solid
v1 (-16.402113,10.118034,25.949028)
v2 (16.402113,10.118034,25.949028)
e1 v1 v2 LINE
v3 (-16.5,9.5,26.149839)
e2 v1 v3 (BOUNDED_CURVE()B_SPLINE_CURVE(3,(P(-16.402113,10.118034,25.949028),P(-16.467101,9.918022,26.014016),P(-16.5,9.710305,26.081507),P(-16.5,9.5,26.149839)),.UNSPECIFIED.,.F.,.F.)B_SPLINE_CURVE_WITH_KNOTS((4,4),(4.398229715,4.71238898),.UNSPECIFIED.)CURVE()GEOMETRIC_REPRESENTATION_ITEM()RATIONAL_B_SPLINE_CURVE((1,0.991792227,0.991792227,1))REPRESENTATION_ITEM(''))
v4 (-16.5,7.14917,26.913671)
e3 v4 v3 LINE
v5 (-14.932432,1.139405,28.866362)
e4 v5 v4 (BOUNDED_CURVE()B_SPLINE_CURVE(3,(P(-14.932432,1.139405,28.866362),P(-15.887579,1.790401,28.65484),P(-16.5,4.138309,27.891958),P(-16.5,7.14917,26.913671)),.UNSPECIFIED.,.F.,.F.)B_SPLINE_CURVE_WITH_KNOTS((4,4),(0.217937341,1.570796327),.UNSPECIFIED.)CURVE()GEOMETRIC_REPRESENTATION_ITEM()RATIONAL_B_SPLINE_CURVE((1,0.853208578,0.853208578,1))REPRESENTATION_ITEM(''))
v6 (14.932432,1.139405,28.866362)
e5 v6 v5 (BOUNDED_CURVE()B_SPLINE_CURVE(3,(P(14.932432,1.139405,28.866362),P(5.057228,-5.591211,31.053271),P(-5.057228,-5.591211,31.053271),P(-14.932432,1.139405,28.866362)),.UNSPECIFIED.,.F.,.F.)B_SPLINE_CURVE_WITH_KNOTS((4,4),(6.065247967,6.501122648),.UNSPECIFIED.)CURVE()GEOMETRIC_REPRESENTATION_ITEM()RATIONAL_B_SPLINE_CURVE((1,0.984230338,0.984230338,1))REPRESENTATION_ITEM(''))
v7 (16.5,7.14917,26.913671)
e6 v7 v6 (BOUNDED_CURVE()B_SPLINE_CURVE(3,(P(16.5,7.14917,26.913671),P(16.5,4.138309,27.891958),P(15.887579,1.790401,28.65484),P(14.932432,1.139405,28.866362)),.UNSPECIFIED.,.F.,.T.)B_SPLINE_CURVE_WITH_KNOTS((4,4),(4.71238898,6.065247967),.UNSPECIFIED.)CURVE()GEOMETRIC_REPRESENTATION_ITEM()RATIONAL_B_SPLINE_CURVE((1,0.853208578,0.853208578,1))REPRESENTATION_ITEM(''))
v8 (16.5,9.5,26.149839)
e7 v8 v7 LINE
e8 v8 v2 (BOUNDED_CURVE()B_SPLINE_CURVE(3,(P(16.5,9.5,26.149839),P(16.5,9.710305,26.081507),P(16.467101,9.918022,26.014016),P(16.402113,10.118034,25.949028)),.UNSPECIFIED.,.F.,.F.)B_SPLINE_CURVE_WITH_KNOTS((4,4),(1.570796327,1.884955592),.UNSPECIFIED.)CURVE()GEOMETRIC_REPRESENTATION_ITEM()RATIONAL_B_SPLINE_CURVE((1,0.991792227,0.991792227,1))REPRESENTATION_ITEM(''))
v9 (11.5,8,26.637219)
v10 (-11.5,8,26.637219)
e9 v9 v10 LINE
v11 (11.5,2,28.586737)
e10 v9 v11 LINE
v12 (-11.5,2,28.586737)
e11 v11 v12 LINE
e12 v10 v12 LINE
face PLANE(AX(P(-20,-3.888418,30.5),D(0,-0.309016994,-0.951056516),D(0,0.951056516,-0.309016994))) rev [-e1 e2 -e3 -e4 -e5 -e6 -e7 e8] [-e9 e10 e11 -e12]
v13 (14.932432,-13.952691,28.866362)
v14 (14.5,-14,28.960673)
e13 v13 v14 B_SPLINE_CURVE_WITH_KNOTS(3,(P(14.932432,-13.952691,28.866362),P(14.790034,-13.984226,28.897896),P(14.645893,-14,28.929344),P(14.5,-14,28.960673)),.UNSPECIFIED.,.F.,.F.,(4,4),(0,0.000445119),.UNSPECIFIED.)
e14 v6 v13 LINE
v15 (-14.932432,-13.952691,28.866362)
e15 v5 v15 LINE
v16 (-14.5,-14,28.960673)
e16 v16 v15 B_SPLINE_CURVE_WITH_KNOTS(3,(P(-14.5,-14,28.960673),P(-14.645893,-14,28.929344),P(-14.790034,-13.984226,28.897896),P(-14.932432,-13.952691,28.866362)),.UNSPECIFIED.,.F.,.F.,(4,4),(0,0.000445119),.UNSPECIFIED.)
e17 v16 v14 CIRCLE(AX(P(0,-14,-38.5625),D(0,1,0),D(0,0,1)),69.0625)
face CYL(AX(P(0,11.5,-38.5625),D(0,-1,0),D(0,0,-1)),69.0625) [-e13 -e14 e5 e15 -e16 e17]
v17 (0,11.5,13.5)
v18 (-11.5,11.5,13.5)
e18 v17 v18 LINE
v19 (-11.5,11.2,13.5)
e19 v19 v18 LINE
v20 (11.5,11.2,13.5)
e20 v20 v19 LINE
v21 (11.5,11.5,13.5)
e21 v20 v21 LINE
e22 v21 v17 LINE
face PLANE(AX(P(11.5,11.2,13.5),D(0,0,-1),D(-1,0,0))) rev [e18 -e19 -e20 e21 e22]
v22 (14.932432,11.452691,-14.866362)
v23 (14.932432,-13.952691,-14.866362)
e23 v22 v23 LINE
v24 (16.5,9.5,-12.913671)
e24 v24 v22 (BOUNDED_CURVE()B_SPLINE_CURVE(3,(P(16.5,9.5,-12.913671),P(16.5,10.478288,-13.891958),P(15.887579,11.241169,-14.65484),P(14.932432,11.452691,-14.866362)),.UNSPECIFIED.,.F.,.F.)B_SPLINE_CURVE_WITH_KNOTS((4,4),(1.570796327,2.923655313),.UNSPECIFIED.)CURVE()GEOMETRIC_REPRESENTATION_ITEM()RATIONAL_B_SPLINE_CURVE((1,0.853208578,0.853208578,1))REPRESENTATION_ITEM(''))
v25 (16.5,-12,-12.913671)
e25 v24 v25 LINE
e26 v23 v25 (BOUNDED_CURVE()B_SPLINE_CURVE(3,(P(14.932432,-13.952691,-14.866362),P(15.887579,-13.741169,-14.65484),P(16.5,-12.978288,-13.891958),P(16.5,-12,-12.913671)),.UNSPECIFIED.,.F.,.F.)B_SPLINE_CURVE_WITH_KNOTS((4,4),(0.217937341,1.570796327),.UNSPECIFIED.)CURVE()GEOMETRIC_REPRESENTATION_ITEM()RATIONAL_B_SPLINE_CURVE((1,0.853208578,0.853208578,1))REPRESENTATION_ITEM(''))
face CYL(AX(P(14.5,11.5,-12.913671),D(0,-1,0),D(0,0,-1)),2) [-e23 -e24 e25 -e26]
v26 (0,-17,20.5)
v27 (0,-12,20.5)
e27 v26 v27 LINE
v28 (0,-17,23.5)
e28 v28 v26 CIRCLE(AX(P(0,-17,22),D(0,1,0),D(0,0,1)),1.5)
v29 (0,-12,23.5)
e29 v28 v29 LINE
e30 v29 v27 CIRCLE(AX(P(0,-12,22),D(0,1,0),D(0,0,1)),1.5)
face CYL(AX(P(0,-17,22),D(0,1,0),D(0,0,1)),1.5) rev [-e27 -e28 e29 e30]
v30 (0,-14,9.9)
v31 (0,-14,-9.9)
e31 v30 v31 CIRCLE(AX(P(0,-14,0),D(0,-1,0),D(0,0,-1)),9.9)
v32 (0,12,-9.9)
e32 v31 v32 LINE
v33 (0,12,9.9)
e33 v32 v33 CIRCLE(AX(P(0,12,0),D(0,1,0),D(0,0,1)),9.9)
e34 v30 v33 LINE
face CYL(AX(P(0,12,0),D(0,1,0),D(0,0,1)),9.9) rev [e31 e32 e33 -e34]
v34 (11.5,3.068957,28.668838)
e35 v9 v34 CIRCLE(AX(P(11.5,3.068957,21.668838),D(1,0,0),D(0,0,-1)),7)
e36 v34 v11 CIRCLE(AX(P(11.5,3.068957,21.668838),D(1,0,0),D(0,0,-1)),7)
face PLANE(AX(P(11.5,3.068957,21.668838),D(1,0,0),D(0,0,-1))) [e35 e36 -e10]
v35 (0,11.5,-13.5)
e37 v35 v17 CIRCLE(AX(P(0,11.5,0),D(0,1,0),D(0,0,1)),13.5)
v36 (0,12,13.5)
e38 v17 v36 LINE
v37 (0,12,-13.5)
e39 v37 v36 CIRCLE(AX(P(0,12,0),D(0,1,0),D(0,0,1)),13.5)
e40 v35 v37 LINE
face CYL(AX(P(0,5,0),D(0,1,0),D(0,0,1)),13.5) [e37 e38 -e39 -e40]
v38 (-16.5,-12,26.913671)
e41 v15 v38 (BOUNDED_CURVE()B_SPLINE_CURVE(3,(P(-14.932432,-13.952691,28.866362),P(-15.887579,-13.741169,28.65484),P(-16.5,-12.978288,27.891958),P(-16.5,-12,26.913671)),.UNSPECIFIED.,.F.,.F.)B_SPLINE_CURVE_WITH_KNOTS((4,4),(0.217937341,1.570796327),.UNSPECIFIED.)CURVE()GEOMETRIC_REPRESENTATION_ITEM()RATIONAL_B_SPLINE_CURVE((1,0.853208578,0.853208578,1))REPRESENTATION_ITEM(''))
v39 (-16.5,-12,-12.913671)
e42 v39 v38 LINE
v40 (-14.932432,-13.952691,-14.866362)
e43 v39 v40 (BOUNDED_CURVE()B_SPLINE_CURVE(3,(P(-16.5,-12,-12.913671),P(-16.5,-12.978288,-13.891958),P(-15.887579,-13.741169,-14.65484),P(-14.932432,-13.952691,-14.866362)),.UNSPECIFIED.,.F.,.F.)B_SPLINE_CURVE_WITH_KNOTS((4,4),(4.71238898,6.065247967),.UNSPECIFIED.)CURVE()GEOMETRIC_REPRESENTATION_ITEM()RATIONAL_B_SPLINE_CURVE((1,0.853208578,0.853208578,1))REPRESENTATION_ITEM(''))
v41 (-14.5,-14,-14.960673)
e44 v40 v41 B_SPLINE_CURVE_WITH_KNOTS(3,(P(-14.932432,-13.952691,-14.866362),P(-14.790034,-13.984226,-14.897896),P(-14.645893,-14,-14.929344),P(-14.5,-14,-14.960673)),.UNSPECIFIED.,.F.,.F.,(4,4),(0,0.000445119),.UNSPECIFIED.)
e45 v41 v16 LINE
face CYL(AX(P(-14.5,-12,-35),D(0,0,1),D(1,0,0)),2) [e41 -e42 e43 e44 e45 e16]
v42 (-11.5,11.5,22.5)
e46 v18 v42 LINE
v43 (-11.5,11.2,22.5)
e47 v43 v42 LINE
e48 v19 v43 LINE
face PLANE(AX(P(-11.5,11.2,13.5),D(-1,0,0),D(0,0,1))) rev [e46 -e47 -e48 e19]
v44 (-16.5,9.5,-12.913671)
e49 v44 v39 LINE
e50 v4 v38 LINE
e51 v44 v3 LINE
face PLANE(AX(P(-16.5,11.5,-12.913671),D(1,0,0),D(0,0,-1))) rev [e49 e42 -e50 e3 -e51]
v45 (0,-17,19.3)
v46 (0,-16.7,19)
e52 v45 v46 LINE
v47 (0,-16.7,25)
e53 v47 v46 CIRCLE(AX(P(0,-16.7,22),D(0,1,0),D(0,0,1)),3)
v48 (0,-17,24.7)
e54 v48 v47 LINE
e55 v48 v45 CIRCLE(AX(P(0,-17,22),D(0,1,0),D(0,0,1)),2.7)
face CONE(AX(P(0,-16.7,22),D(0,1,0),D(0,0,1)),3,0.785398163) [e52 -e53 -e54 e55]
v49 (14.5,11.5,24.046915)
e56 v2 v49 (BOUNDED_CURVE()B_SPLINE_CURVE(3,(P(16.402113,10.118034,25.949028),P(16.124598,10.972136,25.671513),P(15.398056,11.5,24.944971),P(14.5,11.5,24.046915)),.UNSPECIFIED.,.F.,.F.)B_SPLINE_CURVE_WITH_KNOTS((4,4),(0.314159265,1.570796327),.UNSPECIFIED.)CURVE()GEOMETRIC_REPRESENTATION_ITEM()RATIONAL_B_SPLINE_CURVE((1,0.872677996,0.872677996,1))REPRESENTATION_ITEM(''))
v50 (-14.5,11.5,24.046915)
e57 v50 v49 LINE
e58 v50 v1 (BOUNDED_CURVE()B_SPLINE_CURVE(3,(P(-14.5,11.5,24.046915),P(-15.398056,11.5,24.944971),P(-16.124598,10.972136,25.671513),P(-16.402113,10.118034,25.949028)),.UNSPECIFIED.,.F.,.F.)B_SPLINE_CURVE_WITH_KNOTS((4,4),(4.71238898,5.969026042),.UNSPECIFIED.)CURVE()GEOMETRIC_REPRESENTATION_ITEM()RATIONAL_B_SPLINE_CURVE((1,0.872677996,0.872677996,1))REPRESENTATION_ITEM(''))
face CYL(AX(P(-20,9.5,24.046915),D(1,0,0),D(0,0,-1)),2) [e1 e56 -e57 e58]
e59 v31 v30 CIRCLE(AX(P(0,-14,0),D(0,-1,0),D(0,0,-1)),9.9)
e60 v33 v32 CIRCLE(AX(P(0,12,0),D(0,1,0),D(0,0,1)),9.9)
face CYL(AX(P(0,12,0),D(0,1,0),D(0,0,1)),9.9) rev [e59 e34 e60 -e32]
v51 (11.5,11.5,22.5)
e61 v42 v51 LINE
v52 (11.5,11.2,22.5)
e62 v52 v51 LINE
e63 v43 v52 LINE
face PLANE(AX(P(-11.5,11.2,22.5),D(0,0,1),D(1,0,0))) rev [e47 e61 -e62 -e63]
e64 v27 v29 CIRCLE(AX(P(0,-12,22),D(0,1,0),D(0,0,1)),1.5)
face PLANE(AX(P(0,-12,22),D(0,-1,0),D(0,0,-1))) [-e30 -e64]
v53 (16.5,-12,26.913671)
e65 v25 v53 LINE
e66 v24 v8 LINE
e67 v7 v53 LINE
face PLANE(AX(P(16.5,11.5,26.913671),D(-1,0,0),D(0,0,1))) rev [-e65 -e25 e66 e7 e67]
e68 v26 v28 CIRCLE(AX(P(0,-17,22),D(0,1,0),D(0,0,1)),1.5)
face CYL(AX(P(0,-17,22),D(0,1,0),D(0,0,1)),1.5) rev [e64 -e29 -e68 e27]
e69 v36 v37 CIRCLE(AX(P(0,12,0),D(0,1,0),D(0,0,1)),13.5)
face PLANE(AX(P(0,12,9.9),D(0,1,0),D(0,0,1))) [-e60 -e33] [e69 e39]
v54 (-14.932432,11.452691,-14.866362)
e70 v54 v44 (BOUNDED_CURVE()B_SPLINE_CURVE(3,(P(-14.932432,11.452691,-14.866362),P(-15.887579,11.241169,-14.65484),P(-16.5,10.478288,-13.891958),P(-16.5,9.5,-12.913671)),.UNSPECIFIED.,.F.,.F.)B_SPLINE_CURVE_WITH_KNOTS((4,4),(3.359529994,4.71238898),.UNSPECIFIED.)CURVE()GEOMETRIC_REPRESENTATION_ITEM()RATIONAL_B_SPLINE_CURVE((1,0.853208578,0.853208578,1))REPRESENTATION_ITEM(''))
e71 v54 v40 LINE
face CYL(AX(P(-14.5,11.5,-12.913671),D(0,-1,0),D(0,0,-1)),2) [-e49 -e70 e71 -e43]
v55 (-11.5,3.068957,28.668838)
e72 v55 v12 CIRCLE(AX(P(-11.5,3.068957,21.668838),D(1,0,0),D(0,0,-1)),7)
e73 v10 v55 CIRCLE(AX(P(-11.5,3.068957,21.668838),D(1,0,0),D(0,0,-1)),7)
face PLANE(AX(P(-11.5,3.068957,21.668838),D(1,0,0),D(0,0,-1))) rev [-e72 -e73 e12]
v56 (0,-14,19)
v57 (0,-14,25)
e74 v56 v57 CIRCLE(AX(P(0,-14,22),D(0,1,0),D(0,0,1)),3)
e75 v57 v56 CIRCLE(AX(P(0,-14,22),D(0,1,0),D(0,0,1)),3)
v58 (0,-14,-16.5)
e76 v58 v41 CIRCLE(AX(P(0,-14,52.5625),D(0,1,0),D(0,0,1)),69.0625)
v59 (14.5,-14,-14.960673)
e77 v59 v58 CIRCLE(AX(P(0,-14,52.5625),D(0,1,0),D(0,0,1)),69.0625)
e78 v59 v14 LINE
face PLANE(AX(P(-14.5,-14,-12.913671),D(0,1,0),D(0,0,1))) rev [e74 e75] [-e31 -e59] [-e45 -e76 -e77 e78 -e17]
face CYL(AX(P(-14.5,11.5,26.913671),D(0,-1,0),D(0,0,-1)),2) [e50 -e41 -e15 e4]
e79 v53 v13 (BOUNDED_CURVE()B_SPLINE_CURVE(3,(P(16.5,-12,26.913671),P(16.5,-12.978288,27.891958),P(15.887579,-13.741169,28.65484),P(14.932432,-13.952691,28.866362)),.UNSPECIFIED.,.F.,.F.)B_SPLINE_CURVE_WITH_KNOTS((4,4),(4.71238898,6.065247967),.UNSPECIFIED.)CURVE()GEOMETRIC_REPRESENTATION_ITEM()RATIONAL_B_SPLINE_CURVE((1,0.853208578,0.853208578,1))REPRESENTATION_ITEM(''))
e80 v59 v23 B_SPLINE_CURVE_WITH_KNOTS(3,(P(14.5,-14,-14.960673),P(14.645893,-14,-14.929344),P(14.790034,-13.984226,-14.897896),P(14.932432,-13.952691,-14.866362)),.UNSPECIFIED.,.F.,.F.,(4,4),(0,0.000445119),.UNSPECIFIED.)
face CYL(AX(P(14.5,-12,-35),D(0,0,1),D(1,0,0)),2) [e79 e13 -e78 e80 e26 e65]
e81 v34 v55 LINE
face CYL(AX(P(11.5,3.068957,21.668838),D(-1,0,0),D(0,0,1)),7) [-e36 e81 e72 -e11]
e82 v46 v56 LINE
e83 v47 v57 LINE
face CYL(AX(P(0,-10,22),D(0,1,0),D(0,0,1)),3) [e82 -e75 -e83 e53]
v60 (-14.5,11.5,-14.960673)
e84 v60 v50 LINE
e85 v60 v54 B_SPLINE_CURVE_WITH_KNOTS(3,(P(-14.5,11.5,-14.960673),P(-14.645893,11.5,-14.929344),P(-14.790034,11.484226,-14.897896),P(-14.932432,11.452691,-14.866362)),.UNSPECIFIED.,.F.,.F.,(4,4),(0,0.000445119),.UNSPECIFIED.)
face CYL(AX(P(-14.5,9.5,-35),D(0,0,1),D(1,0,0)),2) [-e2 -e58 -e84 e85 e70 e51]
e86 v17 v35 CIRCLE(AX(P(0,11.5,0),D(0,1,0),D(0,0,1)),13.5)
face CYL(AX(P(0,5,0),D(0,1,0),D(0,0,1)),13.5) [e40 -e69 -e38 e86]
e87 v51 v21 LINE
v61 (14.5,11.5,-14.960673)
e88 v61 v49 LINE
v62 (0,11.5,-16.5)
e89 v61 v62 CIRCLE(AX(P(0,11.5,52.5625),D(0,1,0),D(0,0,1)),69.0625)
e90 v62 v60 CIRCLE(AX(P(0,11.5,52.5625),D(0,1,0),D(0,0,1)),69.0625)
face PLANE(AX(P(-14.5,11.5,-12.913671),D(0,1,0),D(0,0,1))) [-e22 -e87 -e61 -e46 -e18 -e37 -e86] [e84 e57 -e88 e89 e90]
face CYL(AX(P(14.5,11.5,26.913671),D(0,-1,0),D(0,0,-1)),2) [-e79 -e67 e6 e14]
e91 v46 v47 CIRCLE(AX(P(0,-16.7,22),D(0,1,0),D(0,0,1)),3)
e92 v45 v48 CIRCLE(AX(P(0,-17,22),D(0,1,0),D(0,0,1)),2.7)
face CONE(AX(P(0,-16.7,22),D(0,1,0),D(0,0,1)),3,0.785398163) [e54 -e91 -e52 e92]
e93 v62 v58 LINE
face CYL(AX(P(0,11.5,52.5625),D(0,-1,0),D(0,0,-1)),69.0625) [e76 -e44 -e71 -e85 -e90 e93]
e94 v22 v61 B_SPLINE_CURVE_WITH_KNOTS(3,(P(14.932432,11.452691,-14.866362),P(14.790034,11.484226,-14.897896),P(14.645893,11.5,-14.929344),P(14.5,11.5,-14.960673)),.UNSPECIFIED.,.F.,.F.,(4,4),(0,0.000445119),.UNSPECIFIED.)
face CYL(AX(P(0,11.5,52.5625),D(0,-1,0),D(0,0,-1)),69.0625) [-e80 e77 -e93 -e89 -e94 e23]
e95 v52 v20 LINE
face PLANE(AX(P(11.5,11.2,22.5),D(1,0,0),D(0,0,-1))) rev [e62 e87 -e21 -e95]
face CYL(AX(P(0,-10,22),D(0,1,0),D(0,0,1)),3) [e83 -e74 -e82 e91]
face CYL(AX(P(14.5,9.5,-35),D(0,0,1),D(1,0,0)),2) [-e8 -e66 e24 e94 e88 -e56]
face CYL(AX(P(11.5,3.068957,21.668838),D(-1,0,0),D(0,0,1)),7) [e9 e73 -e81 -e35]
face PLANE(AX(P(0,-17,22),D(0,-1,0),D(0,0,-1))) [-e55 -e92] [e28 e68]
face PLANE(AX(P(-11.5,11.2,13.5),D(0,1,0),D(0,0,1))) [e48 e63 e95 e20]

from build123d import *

# Parameters (mm, degrees)
EXTRUDE_1_DEPTH          = 20.5
EXTRUDE_START            = -3
EXTRUDE_2_DEPTH          = 3
EXTRUDE_START_2          = -2
EXTRUDE_3_DEPTH          = 2
CUT_EXTRUDE_1_DEPTH      = 35
CUT_EXTRUDE_1_DEPTH_BACK = 35
SKETCH_4_W               = 40
SKETCH_4_H               = 35
SKETCH_6_W               = 9.9
SKETCH_6_H               = 24
SKETCH_7_W               = 9.9
SKETCH_7_H               = 2
CUT_EXTRUDE_2_DEPTH      = 20
CUT_EXTRUDE_2_DEPTH_BACK = 20
SKETCH_8_W               = 3.6
SKETCH_8_H               = 1
SKETCH_10_W              = 1.5
SKETCH_10_H              = 5
EXTRUDE_4_DEPTH          = 11.5
EXTRUDE_4_DEPTH_BACK     = 11.5
SKETCH_12_W              = 23
SKETCH_12_H              = 9
CUT_EXTRUDE_3_DEPTH      = 0.3


with BuildPart() as part:
    # 草图1 → 凸台-拉伸1 (new body)
    with BuildSketch(Plane(origin=(0, -9, 0), x_dir=(-1, 0, 0), z_dir=(0, 1, 0))):
        with BuildLine():
            Line((16.5, -12.913670522), (16.5, 26.913670522))
            ThreePointArc((16.5, 26.913670522), (16.059625735, 28.165695908), (14.932432432, 28.866361535))
            ThreePointArc((14.932432432, 28.866361535), (0, 30.5), (-14.932432432, 28.866361535))
            ThreePointArc((-14.932432432, 28.866361535), (-16.059625735, 28.165695908), (-16.5, 26.913670522))
            Line((-16.5, 26.913670522), (-16.5, -12.913670522))
            ThreePointArc((-16.5, -12.913670522), (-16.059625735, -14.165695908), (-14.932432432, -14.866361535))
            ThreePointArc((-14.932432432, -14.866361535), (0, -16.5), (14.932432432, -14.866361535))
            ThreePointArc((14.932432432, -14.866361535), (16.059625735, -14.165695908), (16.5, -12.913670522))
        make_face()
    extrude(amount=EXTRUDE_1_DEPTH)

    # 草图2 → 凸台-拉伸2 (add)
    with BuildSketch(Plane(origin=(0, -9, 0), x_dir=(-1, 0, 0), z_dir=(0, 1, 0)).offset(EXTRUDE_START)):
        with BuildLine():
            Line((16.5, -12.913670522), (16.5, 26.913670522))
            ThreePointArc((16.5, 26.913670522), (16.059625735, 28.165695908), (14.932432432, 28.866361535))
            ThreePointArc((14.932432432, 28.866361535), (0, 30.5), (-14.932432432, 28.866361535))
            ThreePointArc((-14.932432432, 28.866361535), (-16.059625735, 28.165695908), (-16.5, 26.913670522))
            Line((-16.5, 26.913670522), (-16.5, -12.913670522))
            ThreePointArc((-16.5, -12.913670522), (-16.059625735, -14.165695908), (-14.932432432, -14.866361535))
            ThreePointArc((-14.932432432, -14.866361535), (0, -16.5), (14.932432432, -14.866361535))
            ThreePointArc((14.932432432, -14.866361535), (16.059625735, -14.165695908), (16.5, -12.913670522))
        make_face()
    extrude(amount=EXTRUDE_2_DEPTH)

    # 草图3 → 凸台-拉伸3 (add)
    with BuildSketch(Plane(origin=(0, -12, 0), x_dir=(-1, 0, 0), z_dir=(0, 1, 0)).offset(EXTRUDE_START_2)):
        with BuildLine():
            Line((16.5, -12.913670522), (16.5, 26.913670522))
            ThreePointArc((16.5, 26.913670522), (16.059625735, 28.165695908), (14.932432432, 28.866361535))
            ThreePointArc((14.932432432, 28.866361535), (0, 30.5), (-14.932432432, 28.866361535))
            ThreePointArc((-14.932432432, 28.866361535), (-16.059625735, 28.165695908), (-16.5, 26.913670522))
            Line((-16.5, 26.913670522), (-16.5, -12.913670522))
            ThreePointArc((-16.5, -12.913670522), (-16.059625735, -14.165695908), (-14.932432432, -14.866361535))
            ThreePointArc((-14.932432432, -14.866361535), (0, -16.5), (14.932432432, -14.866361535))
            ThreePointArc((14.932432432, -14.866361535), (16.059625735, -14.165695908), (16.5, -12.913670522))
        make_face()
    extrude(amount=EXTRUDE_3_DEPTH)

    # 草图4 → 切除-拉伸1 (cut, two sides: drawn at the far end of the back side and taken through both)
    with BuildSketch(Plane.XY.offset(-CUT_EXTRUDE_1_DEPTH_BACK)):
        with Locations((0, -2.5)):
            Rectangle(SKETCH_4_W, SKETCH_4_H)
        with BuildLine():
            Line((-16.5, 9.5), (-16.5, -12))
            ThreePointArc((-16.5, -12), (-15.914213562, -13.414213562), (-14.5, -14))
            Line((-14.5, -14), (14.5, -14))
            ThreePointArc((14.5, -14), (15.914213562, -13.414213562), (16.5, -12))
            Line((16.5, -12), (16.5, 9.5))
            ThreePointArc((16.5, 9.5), (15.914213562, 10.914213562), (14.5, 11.5))
            Line((14.5, 11.5), (-14.5, 11.5))
            ThreePointArc((-14.5, 11.5), (-15.914213562, 10.914213562), (-16.5, 9.5))
        make_face(mode=Mode.SUBTRACT)
    extrude(amount=CUT_EXTRUDE_1_DEPTH + CUT_EXTRUDE_1_DEPTH_BACK, mode=Mode.SUBTRACT)

    # 草图6 → 切除-旋转1 (revolve, cut)
    with BuildSketch(Plane(origin=(0, 0, 0), x_dir=(0, 0, -1), z_dir=(1, 0, 0))):
        with Locations((-4.95, 0)):
            Rectangle(SKETCH_6_W, SKETCH_6_H)
    revolve(axis=Axis((0, 12, 0), (0, -1, 0)), mode=Mode.SUBTRACT)

    # 草图7 → 切除-旋转2 (revolve, cut)
    with BuildSketch(Plane(origin=(0, 0, 0), x_dir=(0, 0, -1), z_dir=(1, 0, 0))):
        with Locations((-4.95, -13)):
            Rectangle(SKETCH_7_W, SKETCH_7_H)
    revolve(axis=Axis((0, -12, 0), (0, -1, 0)), mode=Mode.SUBTRACT)

    # 草图9 → 切除-拉伸2 (cut, two sides: drawn at the far end of the back side and taken through both)
    with BuildSketch(Plane(origin=(0, 0, 0), x_dir=(0, 0, -1), z_dir=(1, 0, 0)).offset(-CUT_EXTRUDE_2_DEPTH_BACK)):
        with BuildLine():
            Line((-35, -25), (-15, -25))
            Line((-15, -25), (-15, -14))
            Line((-15, -14), (-30.5, -14))
            Line((-30.5, -14), (-30.5, -3.888417686))
            Line((-30.5, -3.888417686), (-25.949027977, 10.118033989))
            ThreePointArc((-25.949027977, 10.118033989), (-25.222485449, 11.118033989), (-24.046914944, 11.5))
            Line((-24.046914944, 11.5), (-15, 11.5))
            Line((-15, 11.5), (-15, 25))
            Line((-15, 25), (-35, 25))
            Line((-35, 25), (-35, -25))
        make_face()
    extrude(amount=CUT_EXTRUDE_2_DEPTH + CUT_EXTRUDE_2_DEPTH_BACK, mode=Mode.SUBTRACT)

    # 草图8 → 旋转1 (revolve)
    with BuildSketch(Plane(origin=(0, 0, 0), x_dir=(0, 0, -1), z_dir=(1, 0, 0))):
        with Locations((-11.7, 11.5)):
            Rectangle(SKETCH_8_W, SKETCH_8_H)
    revolve(axis=Axis((0, 5, 0), (0, -1, 0)))

    # 草图5 → 旋转2 (revolve)
    with BuildSketch(Plane(origin=(0, 0, 0), x_dir=(0, 0, -1), z_dir=(1, 0, 0))):
        Polygon((-22, -17), (-24.7, -17), (-25, -16.7), (-25, -10), (-22, -10), align=None)
    revolve(axis=Axis((0, -10, 22), (0, -1, 0)))

    # 草图10 → 切除-旋转3 (revolve, cut)
    with BuildSketch(Plane(origin=(0, 0, 0), x_dir=(0, 0, -1), z_dir=(1, 0, 0)), mode=Mode.PRIVATE) as cut_revolve_3_sk:
        with Locations((-21.25, -14.5)):
            Rectangle(SKETCH_10_W, SKETCH_10_H)
    revolve(cut_revolve_3_sk.sketch.rotate(Axis((0, -17, 22), (0, 1, 0)), 180), axis=Axis((0, -17, 22), (0, 1, 0)), mode=Mode.SUBTRACT)

    # 草图11 → 凸台-拉伸4 (add, two sides: drawn at the far end of the back side and taken through both)
    with BuildSketch(Plane(origin=(0, 0, 0), x_dir=(0, 0, -1), z_dir=(1, 0, 0)).offset(-EXTRUDE_4_DEPTH_BACK)):
        with BuildLine():
            Line((-28.586737114, 2), (-26, 2))
            Line((-26, 2), (-26, 8))
            Line((-26, 8), (-26.637218937, 8))
            ThreePointArc((-26.637218937, 8), (-28.326233362, 5.232075627), (-28.586737114, 2))
        make_face()
    extrude(amount=EXTRUDE_4_DEPTH + EXTRUDE_4_DEPTH_BACK)

    # 草图12 → 切除-拉伸3 (cut)
    with BuildSketch(Plane(origin=(0, 11.5, 0), x_dir=(-1, 0, 0), z_dir=(0, 1, 0))):
        with Locations((0, 18)):
            Rectangle(SKETCH_12_W, SKETCH_12_H)
    extrude(amount=-CUT_EXTRUDE_3_DEPTH, mode=Mode.SUBTRACT)


solid = part.part
